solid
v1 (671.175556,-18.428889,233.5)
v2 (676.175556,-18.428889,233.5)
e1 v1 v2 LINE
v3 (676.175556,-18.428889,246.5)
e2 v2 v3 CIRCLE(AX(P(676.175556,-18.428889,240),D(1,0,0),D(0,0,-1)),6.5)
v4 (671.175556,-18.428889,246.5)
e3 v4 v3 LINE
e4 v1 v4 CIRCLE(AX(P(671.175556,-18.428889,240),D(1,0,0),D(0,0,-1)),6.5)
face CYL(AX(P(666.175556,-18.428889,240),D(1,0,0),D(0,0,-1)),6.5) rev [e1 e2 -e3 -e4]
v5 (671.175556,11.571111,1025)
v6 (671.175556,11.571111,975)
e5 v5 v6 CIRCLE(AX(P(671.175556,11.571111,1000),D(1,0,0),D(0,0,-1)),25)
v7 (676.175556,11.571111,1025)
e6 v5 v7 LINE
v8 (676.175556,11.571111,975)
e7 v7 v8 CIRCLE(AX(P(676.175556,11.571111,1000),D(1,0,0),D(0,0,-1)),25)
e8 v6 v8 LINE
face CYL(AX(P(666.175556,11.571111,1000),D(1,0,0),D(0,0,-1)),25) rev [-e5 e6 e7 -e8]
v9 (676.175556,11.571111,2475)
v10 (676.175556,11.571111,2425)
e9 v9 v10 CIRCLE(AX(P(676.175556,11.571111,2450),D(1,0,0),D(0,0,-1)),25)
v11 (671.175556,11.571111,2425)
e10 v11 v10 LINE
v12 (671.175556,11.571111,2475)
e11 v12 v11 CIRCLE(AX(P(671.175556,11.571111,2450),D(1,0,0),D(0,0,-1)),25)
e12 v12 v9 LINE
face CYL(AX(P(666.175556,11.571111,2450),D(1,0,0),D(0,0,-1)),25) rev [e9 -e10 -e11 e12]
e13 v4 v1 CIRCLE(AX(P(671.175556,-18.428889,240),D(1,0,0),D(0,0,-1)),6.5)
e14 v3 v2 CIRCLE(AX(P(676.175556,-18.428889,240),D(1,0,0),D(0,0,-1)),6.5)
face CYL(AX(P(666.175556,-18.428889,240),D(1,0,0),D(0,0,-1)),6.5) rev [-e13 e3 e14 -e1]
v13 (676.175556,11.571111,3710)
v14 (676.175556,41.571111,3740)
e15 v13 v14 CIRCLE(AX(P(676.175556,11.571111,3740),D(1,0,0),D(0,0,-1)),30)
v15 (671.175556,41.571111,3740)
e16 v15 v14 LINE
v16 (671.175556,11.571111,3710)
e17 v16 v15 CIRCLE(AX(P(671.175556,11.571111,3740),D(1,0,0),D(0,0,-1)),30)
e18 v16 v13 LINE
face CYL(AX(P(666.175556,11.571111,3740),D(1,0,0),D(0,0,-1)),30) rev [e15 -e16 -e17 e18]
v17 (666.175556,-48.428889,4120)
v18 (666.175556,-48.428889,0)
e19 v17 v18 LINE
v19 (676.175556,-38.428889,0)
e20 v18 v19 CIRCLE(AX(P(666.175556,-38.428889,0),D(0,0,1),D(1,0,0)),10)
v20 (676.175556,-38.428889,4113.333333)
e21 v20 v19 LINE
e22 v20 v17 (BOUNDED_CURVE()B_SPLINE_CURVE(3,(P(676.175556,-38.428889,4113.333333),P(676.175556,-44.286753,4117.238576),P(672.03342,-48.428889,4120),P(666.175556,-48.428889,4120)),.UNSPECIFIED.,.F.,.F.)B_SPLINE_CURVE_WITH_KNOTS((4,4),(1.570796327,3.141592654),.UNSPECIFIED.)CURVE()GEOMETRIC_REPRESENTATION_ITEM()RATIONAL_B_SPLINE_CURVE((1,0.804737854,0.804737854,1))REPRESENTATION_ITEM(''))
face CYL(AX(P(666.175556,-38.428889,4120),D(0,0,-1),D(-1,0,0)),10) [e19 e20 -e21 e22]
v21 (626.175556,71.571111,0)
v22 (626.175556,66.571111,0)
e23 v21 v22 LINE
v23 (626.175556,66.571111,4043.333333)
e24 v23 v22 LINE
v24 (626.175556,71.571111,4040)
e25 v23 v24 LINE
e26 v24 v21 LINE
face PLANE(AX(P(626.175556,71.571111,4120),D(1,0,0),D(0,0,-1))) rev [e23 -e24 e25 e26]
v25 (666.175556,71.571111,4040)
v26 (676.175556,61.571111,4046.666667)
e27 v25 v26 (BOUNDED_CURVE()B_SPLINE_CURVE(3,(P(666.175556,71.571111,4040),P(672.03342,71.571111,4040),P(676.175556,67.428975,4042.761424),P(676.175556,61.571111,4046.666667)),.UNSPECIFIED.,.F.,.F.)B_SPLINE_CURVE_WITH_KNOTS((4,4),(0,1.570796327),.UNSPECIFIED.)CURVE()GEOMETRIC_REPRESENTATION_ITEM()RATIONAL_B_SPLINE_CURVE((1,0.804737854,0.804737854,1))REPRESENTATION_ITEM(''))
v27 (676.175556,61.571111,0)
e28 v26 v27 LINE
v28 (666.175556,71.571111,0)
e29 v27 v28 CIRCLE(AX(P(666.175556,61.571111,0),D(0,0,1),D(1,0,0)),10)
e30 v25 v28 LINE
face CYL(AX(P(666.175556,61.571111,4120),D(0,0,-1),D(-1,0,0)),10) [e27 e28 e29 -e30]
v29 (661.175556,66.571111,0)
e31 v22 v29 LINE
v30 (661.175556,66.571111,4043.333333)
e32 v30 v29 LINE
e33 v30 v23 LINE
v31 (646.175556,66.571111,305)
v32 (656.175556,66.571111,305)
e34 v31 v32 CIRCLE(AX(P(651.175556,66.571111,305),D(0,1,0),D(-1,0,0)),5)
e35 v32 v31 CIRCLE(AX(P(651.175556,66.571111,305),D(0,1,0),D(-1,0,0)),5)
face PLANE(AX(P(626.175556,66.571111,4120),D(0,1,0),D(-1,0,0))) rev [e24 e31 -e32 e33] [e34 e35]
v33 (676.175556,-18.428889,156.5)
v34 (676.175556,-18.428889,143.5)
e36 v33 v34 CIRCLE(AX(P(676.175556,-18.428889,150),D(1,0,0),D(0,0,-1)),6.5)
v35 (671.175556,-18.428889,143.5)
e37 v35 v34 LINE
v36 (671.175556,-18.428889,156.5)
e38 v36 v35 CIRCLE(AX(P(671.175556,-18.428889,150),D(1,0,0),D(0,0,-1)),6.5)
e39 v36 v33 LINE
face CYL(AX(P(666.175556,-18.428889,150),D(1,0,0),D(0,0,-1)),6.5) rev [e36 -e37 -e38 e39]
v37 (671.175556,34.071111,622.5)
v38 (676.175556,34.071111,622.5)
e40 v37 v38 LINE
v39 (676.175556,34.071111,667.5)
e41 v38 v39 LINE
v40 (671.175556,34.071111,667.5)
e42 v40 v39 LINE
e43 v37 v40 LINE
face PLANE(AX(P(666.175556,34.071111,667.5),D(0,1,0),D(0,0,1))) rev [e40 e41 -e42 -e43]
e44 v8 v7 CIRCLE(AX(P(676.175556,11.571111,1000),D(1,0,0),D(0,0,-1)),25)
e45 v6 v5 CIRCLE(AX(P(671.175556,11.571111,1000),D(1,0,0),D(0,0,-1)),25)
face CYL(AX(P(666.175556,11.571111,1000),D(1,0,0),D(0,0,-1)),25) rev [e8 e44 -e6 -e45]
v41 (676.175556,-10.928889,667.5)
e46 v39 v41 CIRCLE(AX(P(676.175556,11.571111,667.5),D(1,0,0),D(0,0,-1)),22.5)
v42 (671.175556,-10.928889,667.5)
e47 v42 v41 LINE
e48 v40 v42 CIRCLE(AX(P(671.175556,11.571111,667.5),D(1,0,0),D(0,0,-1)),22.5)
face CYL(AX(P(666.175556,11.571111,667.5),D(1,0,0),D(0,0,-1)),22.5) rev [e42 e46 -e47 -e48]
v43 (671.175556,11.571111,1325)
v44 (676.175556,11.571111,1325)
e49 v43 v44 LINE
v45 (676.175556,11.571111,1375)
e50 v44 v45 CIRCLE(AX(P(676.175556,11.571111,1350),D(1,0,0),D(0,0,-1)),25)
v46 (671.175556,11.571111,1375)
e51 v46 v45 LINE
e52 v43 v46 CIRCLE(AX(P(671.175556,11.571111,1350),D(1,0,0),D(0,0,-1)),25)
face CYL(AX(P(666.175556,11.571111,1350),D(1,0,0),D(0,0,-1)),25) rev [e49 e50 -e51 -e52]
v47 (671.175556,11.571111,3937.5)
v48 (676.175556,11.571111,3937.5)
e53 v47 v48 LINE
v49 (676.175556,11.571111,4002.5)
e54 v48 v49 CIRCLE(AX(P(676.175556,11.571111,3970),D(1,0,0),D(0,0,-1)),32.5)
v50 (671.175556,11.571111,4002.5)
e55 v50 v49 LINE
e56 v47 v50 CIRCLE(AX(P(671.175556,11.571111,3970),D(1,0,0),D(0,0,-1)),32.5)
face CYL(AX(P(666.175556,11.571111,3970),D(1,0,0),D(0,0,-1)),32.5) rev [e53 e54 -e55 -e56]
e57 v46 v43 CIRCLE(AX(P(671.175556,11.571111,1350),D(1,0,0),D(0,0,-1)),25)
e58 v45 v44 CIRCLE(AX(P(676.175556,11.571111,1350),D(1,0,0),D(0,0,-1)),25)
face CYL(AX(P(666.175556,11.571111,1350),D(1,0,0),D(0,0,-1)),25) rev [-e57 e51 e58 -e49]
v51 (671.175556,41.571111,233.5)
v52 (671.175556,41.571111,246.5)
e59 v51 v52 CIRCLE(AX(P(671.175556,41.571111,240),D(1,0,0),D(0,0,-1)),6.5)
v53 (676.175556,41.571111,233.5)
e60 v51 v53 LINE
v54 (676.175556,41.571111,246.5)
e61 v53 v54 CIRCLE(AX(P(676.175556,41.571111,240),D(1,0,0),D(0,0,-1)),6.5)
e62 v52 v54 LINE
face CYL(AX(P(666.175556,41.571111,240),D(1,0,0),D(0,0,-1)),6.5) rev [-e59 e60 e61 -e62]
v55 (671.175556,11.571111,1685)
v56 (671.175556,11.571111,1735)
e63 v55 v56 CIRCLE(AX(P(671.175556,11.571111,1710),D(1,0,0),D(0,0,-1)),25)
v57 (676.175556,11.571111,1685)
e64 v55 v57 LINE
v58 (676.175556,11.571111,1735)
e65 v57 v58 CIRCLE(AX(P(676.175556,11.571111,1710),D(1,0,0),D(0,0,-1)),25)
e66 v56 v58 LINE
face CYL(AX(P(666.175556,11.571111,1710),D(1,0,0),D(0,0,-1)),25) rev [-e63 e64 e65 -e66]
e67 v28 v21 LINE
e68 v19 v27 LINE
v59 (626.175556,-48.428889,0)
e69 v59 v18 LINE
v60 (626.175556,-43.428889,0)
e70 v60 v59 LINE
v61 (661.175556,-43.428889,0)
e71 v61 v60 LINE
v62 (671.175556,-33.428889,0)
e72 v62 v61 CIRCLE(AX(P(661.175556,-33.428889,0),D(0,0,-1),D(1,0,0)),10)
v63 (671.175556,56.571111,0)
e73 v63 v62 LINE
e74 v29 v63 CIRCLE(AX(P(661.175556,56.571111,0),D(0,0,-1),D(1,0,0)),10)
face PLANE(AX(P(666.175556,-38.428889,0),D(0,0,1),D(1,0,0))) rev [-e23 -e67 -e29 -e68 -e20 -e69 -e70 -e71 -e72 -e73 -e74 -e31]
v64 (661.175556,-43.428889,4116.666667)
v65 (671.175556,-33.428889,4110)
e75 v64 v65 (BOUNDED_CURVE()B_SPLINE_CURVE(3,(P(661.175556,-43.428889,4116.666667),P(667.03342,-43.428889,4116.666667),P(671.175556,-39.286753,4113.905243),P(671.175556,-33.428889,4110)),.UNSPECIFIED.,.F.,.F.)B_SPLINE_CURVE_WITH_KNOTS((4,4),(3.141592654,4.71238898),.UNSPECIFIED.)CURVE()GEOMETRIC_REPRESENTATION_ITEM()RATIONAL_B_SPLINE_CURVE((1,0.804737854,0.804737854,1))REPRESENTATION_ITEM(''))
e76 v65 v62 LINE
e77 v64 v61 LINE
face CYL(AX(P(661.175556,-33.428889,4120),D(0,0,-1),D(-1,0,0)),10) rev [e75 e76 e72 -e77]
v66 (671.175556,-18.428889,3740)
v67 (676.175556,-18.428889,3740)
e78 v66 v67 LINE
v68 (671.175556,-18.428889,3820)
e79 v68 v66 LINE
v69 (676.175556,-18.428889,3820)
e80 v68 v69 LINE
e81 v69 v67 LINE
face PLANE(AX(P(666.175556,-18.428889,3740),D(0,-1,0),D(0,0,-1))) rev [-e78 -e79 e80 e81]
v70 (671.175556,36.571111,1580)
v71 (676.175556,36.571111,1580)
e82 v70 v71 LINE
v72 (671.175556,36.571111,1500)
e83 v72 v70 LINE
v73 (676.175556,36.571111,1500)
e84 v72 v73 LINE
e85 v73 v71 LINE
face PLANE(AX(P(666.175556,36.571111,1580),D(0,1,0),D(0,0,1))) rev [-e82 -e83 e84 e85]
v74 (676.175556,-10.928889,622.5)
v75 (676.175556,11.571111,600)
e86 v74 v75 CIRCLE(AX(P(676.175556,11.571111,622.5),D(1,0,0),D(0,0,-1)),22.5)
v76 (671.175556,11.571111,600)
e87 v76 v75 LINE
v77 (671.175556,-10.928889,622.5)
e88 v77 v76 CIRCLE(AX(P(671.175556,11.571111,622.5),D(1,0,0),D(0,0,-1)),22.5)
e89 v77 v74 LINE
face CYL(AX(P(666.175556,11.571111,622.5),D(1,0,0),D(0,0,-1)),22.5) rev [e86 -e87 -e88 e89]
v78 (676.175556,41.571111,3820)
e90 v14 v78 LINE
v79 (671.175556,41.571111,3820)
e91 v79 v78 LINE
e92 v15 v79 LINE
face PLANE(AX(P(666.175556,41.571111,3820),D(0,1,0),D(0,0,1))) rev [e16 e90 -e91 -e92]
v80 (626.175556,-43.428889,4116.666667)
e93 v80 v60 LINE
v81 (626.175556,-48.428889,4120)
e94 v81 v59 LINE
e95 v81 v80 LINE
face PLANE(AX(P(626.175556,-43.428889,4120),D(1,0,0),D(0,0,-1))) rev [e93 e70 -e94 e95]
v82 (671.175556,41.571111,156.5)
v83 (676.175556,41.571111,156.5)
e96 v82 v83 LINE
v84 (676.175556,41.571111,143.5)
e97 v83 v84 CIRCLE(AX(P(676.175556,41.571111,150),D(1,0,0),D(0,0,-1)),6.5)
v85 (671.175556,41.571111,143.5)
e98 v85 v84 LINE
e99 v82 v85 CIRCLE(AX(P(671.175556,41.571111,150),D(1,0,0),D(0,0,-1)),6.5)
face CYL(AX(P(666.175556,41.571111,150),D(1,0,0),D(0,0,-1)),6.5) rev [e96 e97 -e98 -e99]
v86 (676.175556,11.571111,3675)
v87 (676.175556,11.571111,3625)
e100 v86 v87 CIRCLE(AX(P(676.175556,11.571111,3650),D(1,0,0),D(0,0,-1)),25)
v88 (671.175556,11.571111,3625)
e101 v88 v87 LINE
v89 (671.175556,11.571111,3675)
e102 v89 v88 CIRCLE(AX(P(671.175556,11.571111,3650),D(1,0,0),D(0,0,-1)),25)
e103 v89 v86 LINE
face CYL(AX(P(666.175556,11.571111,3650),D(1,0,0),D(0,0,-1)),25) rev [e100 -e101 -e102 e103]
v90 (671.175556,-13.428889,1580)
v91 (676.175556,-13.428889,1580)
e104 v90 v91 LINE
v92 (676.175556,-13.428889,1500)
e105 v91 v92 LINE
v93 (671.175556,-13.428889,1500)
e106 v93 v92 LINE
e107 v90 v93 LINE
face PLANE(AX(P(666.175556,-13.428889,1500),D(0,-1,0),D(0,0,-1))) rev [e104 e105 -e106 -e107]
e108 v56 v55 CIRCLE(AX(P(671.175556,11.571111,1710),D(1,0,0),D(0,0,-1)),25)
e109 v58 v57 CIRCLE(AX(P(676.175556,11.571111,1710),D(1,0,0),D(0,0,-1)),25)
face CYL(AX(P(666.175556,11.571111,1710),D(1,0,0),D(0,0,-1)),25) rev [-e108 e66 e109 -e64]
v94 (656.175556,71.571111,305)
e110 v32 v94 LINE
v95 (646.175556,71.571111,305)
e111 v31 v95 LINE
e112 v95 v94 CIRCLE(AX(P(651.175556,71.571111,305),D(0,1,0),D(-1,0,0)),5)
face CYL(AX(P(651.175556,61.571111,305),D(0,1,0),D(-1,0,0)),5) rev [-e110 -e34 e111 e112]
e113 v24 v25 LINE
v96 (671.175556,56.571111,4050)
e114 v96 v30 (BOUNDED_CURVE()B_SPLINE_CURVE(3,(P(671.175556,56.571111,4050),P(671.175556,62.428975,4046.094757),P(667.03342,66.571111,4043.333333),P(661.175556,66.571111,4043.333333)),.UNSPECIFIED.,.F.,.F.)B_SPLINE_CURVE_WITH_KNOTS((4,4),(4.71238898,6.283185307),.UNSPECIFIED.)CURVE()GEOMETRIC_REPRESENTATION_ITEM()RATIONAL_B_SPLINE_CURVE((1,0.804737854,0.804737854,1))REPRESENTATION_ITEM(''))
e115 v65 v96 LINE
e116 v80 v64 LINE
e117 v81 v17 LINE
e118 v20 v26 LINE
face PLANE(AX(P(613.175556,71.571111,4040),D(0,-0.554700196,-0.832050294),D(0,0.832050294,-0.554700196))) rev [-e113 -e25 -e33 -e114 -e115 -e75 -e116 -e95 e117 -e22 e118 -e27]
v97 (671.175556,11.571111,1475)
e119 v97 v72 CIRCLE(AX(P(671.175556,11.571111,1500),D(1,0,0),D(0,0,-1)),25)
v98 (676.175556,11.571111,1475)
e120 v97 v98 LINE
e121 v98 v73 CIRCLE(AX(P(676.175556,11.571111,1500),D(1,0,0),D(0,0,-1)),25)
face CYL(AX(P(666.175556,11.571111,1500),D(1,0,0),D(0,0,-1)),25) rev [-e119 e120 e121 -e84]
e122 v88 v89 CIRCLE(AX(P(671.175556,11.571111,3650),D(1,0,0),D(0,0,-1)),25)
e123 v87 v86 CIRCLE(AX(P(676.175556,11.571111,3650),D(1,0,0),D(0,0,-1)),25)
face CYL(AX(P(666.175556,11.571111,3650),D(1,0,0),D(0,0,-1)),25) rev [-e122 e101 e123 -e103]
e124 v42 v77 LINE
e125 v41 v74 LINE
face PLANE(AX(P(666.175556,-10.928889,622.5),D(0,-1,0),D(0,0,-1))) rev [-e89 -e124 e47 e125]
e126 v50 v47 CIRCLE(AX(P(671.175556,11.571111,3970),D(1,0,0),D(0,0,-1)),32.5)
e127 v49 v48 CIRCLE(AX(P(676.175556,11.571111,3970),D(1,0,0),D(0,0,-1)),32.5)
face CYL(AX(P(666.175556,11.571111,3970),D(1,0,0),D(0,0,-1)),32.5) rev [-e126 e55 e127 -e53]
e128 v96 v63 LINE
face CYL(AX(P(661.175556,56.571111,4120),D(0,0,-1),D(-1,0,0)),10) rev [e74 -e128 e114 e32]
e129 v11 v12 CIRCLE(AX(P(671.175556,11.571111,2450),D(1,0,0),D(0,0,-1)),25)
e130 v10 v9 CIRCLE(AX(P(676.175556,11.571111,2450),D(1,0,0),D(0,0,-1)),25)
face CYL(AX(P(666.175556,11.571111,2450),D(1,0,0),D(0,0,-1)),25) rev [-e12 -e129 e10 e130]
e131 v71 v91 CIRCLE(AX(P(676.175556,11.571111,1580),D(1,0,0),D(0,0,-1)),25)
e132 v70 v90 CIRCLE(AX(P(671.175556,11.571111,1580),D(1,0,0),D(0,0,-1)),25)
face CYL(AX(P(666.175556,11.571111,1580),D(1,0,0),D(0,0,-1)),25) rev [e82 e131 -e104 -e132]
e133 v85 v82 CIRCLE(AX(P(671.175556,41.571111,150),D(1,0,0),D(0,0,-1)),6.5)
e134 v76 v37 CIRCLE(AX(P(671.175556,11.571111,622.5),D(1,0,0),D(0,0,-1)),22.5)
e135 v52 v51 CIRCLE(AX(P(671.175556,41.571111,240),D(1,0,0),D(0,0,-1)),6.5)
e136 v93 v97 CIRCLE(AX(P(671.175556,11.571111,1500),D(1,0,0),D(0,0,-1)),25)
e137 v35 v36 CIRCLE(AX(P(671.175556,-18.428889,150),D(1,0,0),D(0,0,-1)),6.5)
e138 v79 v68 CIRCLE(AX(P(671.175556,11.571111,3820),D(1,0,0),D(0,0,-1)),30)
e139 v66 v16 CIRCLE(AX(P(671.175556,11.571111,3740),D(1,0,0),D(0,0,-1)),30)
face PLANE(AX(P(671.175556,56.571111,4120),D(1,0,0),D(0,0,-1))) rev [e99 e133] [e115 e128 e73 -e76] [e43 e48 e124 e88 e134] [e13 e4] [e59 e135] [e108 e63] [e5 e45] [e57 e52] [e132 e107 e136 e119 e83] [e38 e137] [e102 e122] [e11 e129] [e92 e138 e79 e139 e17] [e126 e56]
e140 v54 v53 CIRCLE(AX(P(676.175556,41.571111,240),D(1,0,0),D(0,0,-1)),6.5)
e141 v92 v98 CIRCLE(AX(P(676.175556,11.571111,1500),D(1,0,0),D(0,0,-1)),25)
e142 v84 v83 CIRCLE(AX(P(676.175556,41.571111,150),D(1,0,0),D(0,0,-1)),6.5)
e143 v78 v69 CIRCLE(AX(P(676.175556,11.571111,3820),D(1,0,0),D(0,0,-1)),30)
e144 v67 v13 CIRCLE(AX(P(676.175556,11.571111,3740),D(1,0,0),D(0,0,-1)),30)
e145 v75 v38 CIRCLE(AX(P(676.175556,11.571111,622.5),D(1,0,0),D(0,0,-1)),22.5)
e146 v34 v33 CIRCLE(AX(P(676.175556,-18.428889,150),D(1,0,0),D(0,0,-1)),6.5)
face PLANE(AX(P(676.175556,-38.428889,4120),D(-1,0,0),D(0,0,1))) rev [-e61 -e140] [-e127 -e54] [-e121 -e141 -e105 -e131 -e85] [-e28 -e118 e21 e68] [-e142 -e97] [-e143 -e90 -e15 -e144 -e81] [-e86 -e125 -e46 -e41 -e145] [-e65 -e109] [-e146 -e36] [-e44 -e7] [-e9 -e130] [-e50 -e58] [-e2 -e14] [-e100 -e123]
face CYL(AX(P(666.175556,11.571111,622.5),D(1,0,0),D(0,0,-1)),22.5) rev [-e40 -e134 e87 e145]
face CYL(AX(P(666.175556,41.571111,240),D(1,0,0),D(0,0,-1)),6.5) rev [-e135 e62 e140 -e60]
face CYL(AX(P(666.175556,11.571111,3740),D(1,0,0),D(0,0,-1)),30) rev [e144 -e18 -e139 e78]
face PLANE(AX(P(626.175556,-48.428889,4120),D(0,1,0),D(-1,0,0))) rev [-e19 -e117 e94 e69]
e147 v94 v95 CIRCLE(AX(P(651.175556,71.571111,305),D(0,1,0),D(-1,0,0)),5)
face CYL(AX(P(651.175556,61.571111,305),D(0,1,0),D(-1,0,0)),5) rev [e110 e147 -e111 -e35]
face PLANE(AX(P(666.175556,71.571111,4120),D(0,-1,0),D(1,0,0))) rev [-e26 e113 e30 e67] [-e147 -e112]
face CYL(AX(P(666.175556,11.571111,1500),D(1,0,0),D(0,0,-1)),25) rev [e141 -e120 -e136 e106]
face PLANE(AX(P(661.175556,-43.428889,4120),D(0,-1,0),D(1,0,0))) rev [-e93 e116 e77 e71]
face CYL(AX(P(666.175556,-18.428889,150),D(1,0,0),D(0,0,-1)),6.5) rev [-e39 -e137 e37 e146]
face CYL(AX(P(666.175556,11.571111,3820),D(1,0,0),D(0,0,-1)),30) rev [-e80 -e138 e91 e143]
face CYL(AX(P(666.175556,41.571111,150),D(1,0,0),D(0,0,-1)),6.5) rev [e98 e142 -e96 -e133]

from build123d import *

# Parameters (mm, degrees)
EXTRUDE_1_DEPTH     = 4120
SKETCH_2_R          = 5
CUT_EXTRUDE_1_DEPTH = 10
SKETCH_3_R          = 6.5
SKETCH_3_R_2        = 25
SKETCH_3_R_3        = 22.5
CUT_EXTRUDE_2_DEPTH = 10
CUT_EXTRUDE_3_DEPTH = 10
SKETCH_5_R          = 6.5
CUT_EXTRUDE_4_DEPTH = 10
EXTRUDE_4_DEPTH     = 5
SKETCH_7_R          = 32.5
CUT_EXTRUDE_5_DEPTH = 10
CUT_EXTRUDE_6_DEPTH = 63


with BuildPart() as part:
    # 草图1 → 凸台-拉伸1 (new body)
    with BuildSketch(Plane.XY):
        with BuildLine():
            Line((626.175555556, -48.428888889), (666.175555556, -48.428888889))
            ThreePointArc((666.175555556, -48.428888889), (673.246623367, -45.499956701), (676.175555556, -38.428888889))
            Line((676.175555556, -38.428888889), (676.175555556, 61.571111111))
            ThreePointArc((676.175555556, 61.571111111), (673.246623367, 68.642178923), (666.175555556, 71.571111111))
            Line((666.175555556, 71.571111111), (626.175555556, 71.571111111))
            Line((626.175555556, 71.571111111), (626.175555556, 66.571111111))
            Line((626.175555556, 66.571111111), (661.175555556, 66.571111111))
            ThreePointArc((661.175555556, 66.571111111), (668.246623367, 63.642178923), (671.175555556, 56.571111111))
            Line((671.175555556, 56.571111111), (671.175555556, -33.428888889))
            ThreePointArc((671.175555556, -33.428888889), (668.246623367, -40.499956701), (661.175555556, -43.428888889))
            Line((661.175555556, -43.428888889), (626.175555556, -43.428888889))
            Line((626.175555556, -43.428888889), (626.175555556, -48.428888889))
        make_face()
    extrude(amount=EXTRUDE_1_DEPTH)

    # 草图2 → 切除-拉伸1 (cut)
    with BuildSketch(Plane(origin=(0, 71.571111111, 0), x_dir=(1, 0, 0), z_dir=(0, 1, 0))):
        with Locations(Location((651.175555556, -305, 0), (0, 0, 180))):
            Circle(SKETCH_2_R)
    extrude(amount=-CUT_EXTRUDE_1_DEPTH, mode=Mode.SUBTRACT)

    # 草图3 → 切除-拉伸2 (cut)
    with BuildSketch(Plane(origin=(676.175555556, 0, 0), x_dir=(0, 0, -1), z_dir=(1, 0, 0))):
        with Locations((-225, 41.571111111)):
            Circle(SKETCH_3_R)
        with Locations((-135, 41.571111111)):
            Circle(SKETCH_3_R)
        with Locations((-135, -18.428888889)):
            Circle(SKETCH_3_R)
        with Locations((-225, -18.428888889)):
            Circle(SKETCH_3_R)
        with Locations((-1000, 11.571111111)):
            Circle(SKETCH_3_R_2)
        with Locations((-1350, 11.571111111)):
            Circle(SKETCH_3_R_2)
        with Locations((-3970, 11.571111111)):
            Circle(SKETCH_3_R_3)
        with Locations((-3650, 11.571111111)):
            Circle(SKETCH_3_R_2)
        with Locations((-1710, 11.571111111)):
            Circle(SKETCH_3_R_2)
        with Locations((-2450, 11.571111111)):
            Circle(SKETCH_3_R_2)
        with BuildLine():
            Line((-667.5, 34.071111111), (-622.5, 34.071111111))
            ThreePointArc((-622.5, 34.071111111), (-600, 11.571111111), (-622.5, -10.928888889))
            Line((-622.5, -10.928888889), (-667.5, -10.928888889))
            ThreePointArc((-667.5, -10.928888889), (-690, 11.571111111), (-667.5, 34.071111111))
        make_face()
        with BuildLine():
            Line((-3820, 41.571111111), (-3740, 41.571111111))
            ThreePointArc((-3740, 41.571111111), (-3710, 11.571111111), (-3740, -18.428888889))
            Line((-3740, -18.428888889), (-3820, -18.428888889))
            ThreePointArc((-3820, -18.428888889), (-3850, 11.571111111), (-3820, 41.571111111))
        make_face()
    extrude(amount=-CUT_EXTRUDE_2_DEPTH, mode=Mode.SUBTRACT)

    # 草图4 → 切除-拉伸3 (cut)
    with BuildSketch(Plane(origin=(676.175555556, 0, 0), x_dir=(0, 0, -1), z_dir=(1, 0, 0))):
        with BuildLine():
            Line((-1580, 36.571111111), (-1500, 36.571111111))
            ThreePointArc((-1500, 36.571111111), (-1475, 11.571111111), (-1500, -13.428888889))
            Line((-1500, -13.428888889), (-1580, -13.428888889))
            ThreePointArc((-1580, -13.428888889), (-1605, 11.571111111), (-1580, 36.571111111))
        make_face()
    extrude(amount=-CUT_EXTRUDE_3_DEPTH, mode=Mode.SUBTRACT)

    # 草图5 → 切除-拉伸4 (cut)
    with BuildSketch(Plane(origin=(676.175555556, 0, 0), x_dir=(0, 0, -1), z_dir=(1, 0, 0))):
        with Locations((-150, 41.571111111)):
            Circle(SKETCH_5_R)
        with Locations((-150, -18.428888889)):
            Circle(SKETCH_5_R)
        with Locations((-240, -18.428888889)):
            Circle(SKETCH_5_R)
        with Locations((-240, 41.571111111)):
            Circle(SKETCH_5_R)
    extrude(amount=-CUT_EXTRUDE_4_DEPTH, mode=Mode.SUBTRACT)

    # 草图6 → 凸台-拉伸4 (add)
    with BuildSketch(Plane(origin=(676.175555556, 0, 0), x_dir=(0, 0, -1), z_dir=(1, 0, 0))):
        Polygon((-232.846363418, 52.773090211), (-232.846363418, -32.197108724), (-210.73029119, -32.197108724), (-210.73029119, 54.281769077), align=None)
        Polygon((-141.939510389, 56.005838269), (-142.912723727, -30.568548212), (-122.771795739, -30.568548212), (-119.310073741, -30.568548212), (-119.310073741, 56.005838269), align=None)
    extrude(amount=-EXTRUDE_4_DEPTH)

    # 草图7 → 切除-拉伸5 (cut)
    with BuildSketch(Plane(origin=(676.175555556, 0, 0), x_dir=(0, 0, -1), z_dir=(1, 0, 0))):
        with Locations((-3970, 11.571111111)):
            Circle(SKETCH_7_R)
    extrude(amount=-CUT_EXTRUDE_5_DEPTH, mode=Mode.SUBTRACT)

    # 草图8 → 切除-拉伸6 (cut)
    with BuildSketch(Plane(origin=(676.175555556, 0, 0), x_dir=(0, 0, -1), z_dir=(1, 0, 0))):
        Polygon((-4120, 71.571111111), (-4040, 71.571111111), (-4120, -48.428888889), align=None)
    extrude(amount=-CUT_EXTRUDE_6_DEPTH, mode=Mode.SUBTRACT)


solid = part.part
